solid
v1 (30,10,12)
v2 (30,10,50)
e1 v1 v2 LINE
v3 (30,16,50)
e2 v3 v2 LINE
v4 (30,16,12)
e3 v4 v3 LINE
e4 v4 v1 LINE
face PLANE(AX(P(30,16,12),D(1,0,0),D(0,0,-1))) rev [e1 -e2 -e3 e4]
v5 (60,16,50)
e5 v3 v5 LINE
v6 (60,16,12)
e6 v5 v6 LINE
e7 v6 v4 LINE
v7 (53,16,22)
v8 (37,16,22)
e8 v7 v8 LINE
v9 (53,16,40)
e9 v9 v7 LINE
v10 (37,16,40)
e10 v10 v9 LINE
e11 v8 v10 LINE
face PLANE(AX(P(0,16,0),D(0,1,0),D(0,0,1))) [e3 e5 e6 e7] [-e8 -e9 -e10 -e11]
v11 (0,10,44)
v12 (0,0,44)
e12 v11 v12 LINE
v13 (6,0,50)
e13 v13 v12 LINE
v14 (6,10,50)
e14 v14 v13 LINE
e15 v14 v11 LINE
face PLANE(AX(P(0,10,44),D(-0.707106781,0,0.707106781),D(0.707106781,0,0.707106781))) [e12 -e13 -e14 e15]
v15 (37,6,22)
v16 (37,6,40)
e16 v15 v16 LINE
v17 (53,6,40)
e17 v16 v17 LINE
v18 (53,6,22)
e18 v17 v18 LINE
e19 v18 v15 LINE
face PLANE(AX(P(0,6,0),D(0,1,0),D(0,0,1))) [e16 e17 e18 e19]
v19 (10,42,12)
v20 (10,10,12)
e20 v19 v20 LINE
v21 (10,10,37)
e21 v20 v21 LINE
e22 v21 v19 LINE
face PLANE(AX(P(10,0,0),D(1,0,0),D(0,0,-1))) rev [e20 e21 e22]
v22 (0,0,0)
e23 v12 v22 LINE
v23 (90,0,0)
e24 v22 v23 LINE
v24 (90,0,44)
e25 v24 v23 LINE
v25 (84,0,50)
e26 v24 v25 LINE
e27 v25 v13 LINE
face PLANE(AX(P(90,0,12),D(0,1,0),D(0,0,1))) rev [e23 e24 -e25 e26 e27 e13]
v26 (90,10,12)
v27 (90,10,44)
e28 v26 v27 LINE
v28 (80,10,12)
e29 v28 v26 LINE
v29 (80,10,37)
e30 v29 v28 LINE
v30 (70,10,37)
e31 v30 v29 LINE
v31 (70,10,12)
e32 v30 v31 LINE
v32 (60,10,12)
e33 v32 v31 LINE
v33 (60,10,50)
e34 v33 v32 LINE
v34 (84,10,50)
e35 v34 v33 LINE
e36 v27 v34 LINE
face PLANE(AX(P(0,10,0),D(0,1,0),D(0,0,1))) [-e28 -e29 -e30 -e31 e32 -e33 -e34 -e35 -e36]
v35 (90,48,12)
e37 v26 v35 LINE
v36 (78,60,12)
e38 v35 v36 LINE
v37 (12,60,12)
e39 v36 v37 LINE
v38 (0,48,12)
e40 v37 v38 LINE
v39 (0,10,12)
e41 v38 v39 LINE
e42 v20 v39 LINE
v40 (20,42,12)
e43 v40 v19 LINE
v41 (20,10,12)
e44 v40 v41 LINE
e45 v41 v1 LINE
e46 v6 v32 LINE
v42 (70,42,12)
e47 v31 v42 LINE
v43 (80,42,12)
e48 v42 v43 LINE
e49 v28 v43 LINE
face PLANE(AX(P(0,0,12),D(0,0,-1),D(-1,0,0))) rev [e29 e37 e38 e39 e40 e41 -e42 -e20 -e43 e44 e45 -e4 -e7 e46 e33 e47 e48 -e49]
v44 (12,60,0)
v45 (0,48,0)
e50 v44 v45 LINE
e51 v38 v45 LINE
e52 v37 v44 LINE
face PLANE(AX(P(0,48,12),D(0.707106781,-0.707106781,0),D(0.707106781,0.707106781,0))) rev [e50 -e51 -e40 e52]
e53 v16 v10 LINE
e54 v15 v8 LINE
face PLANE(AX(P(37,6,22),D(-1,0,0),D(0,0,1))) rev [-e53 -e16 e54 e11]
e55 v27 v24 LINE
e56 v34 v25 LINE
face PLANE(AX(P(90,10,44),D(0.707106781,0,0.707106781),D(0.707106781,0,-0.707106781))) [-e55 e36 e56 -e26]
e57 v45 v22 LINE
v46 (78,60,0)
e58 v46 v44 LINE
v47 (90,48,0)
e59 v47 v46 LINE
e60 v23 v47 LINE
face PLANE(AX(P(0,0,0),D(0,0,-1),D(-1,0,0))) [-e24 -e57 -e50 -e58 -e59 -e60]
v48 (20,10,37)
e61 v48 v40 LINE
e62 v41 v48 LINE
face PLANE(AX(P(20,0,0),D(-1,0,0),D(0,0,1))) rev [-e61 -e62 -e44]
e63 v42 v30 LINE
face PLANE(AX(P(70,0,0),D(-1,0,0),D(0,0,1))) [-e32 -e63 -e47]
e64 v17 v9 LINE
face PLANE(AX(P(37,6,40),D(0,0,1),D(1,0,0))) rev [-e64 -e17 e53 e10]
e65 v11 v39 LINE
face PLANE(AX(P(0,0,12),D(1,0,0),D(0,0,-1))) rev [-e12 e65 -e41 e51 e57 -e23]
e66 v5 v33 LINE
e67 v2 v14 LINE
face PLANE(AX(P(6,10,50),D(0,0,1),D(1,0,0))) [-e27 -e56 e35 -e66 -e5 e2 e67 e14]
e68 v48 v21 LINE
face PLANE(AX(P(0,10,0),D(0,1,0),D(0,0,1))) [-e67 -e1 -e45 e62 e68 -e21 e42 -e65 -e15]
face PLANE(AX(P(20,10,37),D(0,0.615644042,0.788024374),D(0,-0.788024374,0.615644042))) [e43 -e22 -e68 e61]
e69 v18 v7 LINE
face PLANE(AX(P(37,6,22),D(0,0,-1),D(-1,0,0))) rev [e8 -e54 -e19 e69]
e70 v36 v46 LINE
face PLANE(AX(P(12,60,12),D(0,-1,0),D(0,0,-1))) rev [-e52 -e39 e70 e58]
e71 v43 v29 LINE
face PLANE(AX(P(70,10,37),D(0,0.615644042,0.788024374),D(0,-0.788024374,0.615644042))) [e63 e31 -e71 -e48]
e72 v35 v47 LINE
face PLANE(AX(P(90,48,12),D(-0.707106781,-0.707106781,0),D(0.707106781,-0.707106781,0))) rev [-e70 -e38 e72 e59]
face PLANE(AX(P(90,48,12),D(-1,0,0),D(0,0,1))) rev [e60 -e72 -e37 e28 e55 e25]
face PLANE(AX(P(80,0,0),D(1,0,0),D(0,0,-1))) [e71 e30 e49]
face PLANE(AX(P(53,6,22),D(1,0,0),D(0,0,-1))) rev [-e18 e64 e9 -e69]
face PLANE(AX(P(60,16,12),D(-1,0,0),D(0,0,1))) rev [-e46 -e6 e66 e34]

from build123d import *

# Parameters (mm, degrees)
BACK_WALL_DEPTH            = 12
BASE_PLATE_DEPTH           = 10
SQUARE_PAD_PROFILE_30X30_W = 30
SQUARE_PAD_PROFILE_30X30_H = 38
SQUARE_PAD_30X30_DEPTH     = 6
PAD_POCKET_PROFILE_W       = 16
PAD_POCKET_PROFILE_H       = 18
PAD_POCKET_DEPTH           = 10
RIB_1_DEPTH                = 20
RIB_2_DEPTH                = 20
TRIANGULAR_CUT_2_DEPTH     = 10
TRIANGULAR_CUT_1_DEPTH     = 10


with BuildPart() as part:
    # Back Wall Profile → Back Wall (new body)
    with BuildSketch(Plane.XY):
        Polygon((0, 0), (0, 48), (12, 60), (78, 60), (90, 48), (90, 0), align=None)
    extrude(amount=BACK_WALL_DEPTH)

    # Base Plate Profile → Base Plate (add)
    with BuildSketch(Plane.XZ):
        Polygon((90, 12), (0, 12), (0, 44), (6, 50), (84, 50), (90, 44), align=None)
    extrude(amount=-BASE_PLATE_DEPTH)

    # Square Pad Profile 30x30 → Square Pad 30x30 (add)
    with BuildSketch(Plane(origin=(0, 10, 0), x_dir=(1, 0, 0), z_dir=(0, 1, 0))):
        with Locations((45, -31)):
            Rectangle(SQUARE_PAD_PROFILE_30X30_W, SQUARE_PAD_PROFILE_30X30_H)
    extrude(amount=SQUARE_PAD_30X30_DEPTH)

    # Pad Pocket Profile → Pad Pocket (cut)
    with BuildSketch(Plane(origin=(0, 16, 0), x_dir=(1, 0, 0), z_dir=(0, 1, 0))):
        with Locations((45, -31)):
            Rectangle(PAD_POCKET_PROFILE_W, PAD_POCKET_PROFILE_H)
    extrude(amount=-PAD_POCKET_DEPTH, mode=Mode.SUBTRACT)

    # Rib 1 Profile → Rib 1 (add)
    with BuildSketch(Plane.ZY):
        Polygon((12, 10), (12, 42), (37, 10), align=None)
    extrude(amount=-RIB_1_DEPTH)

    # Rib 2 Profile → Rib 2 (add)
    with BuildSketch(Plane(origin=(90, 0, 0), x_dir=(0, 0, -1), z_dir=(1, 0, 0))):
        Polygon((-12, 10), (-12, 42), (-37, 10), align=None)
    extrude(amount=-RIB_2_DEPTH)

    # Triangular Cut 2 Profile → Triangular Cut 2 (cut)
    with BuildSketch(Plane(origin=(90, 0, 0), x_dir=(0, 0, -1), z_dir=(1, 0, 0))):
        Polygon((-12, 42), (-12, 10), (-37, 10), align=None)
    extrude(amount=-TRIANGULAR_CUT_2_DEPTH, mode=Mode.SUBTRACT)

    # Triangular Cut 1 Profile → Triangular Cut 1 (cut)
    with BuildSketch(Plane.ZY):
        Polygon((12, 42), (12, 10), (37, 10), align=None)
    extrude(amount=-TRIANGULAR_CUT_1_DEPTH, mode=Mode.SUBTRACT)


solid = part.part
